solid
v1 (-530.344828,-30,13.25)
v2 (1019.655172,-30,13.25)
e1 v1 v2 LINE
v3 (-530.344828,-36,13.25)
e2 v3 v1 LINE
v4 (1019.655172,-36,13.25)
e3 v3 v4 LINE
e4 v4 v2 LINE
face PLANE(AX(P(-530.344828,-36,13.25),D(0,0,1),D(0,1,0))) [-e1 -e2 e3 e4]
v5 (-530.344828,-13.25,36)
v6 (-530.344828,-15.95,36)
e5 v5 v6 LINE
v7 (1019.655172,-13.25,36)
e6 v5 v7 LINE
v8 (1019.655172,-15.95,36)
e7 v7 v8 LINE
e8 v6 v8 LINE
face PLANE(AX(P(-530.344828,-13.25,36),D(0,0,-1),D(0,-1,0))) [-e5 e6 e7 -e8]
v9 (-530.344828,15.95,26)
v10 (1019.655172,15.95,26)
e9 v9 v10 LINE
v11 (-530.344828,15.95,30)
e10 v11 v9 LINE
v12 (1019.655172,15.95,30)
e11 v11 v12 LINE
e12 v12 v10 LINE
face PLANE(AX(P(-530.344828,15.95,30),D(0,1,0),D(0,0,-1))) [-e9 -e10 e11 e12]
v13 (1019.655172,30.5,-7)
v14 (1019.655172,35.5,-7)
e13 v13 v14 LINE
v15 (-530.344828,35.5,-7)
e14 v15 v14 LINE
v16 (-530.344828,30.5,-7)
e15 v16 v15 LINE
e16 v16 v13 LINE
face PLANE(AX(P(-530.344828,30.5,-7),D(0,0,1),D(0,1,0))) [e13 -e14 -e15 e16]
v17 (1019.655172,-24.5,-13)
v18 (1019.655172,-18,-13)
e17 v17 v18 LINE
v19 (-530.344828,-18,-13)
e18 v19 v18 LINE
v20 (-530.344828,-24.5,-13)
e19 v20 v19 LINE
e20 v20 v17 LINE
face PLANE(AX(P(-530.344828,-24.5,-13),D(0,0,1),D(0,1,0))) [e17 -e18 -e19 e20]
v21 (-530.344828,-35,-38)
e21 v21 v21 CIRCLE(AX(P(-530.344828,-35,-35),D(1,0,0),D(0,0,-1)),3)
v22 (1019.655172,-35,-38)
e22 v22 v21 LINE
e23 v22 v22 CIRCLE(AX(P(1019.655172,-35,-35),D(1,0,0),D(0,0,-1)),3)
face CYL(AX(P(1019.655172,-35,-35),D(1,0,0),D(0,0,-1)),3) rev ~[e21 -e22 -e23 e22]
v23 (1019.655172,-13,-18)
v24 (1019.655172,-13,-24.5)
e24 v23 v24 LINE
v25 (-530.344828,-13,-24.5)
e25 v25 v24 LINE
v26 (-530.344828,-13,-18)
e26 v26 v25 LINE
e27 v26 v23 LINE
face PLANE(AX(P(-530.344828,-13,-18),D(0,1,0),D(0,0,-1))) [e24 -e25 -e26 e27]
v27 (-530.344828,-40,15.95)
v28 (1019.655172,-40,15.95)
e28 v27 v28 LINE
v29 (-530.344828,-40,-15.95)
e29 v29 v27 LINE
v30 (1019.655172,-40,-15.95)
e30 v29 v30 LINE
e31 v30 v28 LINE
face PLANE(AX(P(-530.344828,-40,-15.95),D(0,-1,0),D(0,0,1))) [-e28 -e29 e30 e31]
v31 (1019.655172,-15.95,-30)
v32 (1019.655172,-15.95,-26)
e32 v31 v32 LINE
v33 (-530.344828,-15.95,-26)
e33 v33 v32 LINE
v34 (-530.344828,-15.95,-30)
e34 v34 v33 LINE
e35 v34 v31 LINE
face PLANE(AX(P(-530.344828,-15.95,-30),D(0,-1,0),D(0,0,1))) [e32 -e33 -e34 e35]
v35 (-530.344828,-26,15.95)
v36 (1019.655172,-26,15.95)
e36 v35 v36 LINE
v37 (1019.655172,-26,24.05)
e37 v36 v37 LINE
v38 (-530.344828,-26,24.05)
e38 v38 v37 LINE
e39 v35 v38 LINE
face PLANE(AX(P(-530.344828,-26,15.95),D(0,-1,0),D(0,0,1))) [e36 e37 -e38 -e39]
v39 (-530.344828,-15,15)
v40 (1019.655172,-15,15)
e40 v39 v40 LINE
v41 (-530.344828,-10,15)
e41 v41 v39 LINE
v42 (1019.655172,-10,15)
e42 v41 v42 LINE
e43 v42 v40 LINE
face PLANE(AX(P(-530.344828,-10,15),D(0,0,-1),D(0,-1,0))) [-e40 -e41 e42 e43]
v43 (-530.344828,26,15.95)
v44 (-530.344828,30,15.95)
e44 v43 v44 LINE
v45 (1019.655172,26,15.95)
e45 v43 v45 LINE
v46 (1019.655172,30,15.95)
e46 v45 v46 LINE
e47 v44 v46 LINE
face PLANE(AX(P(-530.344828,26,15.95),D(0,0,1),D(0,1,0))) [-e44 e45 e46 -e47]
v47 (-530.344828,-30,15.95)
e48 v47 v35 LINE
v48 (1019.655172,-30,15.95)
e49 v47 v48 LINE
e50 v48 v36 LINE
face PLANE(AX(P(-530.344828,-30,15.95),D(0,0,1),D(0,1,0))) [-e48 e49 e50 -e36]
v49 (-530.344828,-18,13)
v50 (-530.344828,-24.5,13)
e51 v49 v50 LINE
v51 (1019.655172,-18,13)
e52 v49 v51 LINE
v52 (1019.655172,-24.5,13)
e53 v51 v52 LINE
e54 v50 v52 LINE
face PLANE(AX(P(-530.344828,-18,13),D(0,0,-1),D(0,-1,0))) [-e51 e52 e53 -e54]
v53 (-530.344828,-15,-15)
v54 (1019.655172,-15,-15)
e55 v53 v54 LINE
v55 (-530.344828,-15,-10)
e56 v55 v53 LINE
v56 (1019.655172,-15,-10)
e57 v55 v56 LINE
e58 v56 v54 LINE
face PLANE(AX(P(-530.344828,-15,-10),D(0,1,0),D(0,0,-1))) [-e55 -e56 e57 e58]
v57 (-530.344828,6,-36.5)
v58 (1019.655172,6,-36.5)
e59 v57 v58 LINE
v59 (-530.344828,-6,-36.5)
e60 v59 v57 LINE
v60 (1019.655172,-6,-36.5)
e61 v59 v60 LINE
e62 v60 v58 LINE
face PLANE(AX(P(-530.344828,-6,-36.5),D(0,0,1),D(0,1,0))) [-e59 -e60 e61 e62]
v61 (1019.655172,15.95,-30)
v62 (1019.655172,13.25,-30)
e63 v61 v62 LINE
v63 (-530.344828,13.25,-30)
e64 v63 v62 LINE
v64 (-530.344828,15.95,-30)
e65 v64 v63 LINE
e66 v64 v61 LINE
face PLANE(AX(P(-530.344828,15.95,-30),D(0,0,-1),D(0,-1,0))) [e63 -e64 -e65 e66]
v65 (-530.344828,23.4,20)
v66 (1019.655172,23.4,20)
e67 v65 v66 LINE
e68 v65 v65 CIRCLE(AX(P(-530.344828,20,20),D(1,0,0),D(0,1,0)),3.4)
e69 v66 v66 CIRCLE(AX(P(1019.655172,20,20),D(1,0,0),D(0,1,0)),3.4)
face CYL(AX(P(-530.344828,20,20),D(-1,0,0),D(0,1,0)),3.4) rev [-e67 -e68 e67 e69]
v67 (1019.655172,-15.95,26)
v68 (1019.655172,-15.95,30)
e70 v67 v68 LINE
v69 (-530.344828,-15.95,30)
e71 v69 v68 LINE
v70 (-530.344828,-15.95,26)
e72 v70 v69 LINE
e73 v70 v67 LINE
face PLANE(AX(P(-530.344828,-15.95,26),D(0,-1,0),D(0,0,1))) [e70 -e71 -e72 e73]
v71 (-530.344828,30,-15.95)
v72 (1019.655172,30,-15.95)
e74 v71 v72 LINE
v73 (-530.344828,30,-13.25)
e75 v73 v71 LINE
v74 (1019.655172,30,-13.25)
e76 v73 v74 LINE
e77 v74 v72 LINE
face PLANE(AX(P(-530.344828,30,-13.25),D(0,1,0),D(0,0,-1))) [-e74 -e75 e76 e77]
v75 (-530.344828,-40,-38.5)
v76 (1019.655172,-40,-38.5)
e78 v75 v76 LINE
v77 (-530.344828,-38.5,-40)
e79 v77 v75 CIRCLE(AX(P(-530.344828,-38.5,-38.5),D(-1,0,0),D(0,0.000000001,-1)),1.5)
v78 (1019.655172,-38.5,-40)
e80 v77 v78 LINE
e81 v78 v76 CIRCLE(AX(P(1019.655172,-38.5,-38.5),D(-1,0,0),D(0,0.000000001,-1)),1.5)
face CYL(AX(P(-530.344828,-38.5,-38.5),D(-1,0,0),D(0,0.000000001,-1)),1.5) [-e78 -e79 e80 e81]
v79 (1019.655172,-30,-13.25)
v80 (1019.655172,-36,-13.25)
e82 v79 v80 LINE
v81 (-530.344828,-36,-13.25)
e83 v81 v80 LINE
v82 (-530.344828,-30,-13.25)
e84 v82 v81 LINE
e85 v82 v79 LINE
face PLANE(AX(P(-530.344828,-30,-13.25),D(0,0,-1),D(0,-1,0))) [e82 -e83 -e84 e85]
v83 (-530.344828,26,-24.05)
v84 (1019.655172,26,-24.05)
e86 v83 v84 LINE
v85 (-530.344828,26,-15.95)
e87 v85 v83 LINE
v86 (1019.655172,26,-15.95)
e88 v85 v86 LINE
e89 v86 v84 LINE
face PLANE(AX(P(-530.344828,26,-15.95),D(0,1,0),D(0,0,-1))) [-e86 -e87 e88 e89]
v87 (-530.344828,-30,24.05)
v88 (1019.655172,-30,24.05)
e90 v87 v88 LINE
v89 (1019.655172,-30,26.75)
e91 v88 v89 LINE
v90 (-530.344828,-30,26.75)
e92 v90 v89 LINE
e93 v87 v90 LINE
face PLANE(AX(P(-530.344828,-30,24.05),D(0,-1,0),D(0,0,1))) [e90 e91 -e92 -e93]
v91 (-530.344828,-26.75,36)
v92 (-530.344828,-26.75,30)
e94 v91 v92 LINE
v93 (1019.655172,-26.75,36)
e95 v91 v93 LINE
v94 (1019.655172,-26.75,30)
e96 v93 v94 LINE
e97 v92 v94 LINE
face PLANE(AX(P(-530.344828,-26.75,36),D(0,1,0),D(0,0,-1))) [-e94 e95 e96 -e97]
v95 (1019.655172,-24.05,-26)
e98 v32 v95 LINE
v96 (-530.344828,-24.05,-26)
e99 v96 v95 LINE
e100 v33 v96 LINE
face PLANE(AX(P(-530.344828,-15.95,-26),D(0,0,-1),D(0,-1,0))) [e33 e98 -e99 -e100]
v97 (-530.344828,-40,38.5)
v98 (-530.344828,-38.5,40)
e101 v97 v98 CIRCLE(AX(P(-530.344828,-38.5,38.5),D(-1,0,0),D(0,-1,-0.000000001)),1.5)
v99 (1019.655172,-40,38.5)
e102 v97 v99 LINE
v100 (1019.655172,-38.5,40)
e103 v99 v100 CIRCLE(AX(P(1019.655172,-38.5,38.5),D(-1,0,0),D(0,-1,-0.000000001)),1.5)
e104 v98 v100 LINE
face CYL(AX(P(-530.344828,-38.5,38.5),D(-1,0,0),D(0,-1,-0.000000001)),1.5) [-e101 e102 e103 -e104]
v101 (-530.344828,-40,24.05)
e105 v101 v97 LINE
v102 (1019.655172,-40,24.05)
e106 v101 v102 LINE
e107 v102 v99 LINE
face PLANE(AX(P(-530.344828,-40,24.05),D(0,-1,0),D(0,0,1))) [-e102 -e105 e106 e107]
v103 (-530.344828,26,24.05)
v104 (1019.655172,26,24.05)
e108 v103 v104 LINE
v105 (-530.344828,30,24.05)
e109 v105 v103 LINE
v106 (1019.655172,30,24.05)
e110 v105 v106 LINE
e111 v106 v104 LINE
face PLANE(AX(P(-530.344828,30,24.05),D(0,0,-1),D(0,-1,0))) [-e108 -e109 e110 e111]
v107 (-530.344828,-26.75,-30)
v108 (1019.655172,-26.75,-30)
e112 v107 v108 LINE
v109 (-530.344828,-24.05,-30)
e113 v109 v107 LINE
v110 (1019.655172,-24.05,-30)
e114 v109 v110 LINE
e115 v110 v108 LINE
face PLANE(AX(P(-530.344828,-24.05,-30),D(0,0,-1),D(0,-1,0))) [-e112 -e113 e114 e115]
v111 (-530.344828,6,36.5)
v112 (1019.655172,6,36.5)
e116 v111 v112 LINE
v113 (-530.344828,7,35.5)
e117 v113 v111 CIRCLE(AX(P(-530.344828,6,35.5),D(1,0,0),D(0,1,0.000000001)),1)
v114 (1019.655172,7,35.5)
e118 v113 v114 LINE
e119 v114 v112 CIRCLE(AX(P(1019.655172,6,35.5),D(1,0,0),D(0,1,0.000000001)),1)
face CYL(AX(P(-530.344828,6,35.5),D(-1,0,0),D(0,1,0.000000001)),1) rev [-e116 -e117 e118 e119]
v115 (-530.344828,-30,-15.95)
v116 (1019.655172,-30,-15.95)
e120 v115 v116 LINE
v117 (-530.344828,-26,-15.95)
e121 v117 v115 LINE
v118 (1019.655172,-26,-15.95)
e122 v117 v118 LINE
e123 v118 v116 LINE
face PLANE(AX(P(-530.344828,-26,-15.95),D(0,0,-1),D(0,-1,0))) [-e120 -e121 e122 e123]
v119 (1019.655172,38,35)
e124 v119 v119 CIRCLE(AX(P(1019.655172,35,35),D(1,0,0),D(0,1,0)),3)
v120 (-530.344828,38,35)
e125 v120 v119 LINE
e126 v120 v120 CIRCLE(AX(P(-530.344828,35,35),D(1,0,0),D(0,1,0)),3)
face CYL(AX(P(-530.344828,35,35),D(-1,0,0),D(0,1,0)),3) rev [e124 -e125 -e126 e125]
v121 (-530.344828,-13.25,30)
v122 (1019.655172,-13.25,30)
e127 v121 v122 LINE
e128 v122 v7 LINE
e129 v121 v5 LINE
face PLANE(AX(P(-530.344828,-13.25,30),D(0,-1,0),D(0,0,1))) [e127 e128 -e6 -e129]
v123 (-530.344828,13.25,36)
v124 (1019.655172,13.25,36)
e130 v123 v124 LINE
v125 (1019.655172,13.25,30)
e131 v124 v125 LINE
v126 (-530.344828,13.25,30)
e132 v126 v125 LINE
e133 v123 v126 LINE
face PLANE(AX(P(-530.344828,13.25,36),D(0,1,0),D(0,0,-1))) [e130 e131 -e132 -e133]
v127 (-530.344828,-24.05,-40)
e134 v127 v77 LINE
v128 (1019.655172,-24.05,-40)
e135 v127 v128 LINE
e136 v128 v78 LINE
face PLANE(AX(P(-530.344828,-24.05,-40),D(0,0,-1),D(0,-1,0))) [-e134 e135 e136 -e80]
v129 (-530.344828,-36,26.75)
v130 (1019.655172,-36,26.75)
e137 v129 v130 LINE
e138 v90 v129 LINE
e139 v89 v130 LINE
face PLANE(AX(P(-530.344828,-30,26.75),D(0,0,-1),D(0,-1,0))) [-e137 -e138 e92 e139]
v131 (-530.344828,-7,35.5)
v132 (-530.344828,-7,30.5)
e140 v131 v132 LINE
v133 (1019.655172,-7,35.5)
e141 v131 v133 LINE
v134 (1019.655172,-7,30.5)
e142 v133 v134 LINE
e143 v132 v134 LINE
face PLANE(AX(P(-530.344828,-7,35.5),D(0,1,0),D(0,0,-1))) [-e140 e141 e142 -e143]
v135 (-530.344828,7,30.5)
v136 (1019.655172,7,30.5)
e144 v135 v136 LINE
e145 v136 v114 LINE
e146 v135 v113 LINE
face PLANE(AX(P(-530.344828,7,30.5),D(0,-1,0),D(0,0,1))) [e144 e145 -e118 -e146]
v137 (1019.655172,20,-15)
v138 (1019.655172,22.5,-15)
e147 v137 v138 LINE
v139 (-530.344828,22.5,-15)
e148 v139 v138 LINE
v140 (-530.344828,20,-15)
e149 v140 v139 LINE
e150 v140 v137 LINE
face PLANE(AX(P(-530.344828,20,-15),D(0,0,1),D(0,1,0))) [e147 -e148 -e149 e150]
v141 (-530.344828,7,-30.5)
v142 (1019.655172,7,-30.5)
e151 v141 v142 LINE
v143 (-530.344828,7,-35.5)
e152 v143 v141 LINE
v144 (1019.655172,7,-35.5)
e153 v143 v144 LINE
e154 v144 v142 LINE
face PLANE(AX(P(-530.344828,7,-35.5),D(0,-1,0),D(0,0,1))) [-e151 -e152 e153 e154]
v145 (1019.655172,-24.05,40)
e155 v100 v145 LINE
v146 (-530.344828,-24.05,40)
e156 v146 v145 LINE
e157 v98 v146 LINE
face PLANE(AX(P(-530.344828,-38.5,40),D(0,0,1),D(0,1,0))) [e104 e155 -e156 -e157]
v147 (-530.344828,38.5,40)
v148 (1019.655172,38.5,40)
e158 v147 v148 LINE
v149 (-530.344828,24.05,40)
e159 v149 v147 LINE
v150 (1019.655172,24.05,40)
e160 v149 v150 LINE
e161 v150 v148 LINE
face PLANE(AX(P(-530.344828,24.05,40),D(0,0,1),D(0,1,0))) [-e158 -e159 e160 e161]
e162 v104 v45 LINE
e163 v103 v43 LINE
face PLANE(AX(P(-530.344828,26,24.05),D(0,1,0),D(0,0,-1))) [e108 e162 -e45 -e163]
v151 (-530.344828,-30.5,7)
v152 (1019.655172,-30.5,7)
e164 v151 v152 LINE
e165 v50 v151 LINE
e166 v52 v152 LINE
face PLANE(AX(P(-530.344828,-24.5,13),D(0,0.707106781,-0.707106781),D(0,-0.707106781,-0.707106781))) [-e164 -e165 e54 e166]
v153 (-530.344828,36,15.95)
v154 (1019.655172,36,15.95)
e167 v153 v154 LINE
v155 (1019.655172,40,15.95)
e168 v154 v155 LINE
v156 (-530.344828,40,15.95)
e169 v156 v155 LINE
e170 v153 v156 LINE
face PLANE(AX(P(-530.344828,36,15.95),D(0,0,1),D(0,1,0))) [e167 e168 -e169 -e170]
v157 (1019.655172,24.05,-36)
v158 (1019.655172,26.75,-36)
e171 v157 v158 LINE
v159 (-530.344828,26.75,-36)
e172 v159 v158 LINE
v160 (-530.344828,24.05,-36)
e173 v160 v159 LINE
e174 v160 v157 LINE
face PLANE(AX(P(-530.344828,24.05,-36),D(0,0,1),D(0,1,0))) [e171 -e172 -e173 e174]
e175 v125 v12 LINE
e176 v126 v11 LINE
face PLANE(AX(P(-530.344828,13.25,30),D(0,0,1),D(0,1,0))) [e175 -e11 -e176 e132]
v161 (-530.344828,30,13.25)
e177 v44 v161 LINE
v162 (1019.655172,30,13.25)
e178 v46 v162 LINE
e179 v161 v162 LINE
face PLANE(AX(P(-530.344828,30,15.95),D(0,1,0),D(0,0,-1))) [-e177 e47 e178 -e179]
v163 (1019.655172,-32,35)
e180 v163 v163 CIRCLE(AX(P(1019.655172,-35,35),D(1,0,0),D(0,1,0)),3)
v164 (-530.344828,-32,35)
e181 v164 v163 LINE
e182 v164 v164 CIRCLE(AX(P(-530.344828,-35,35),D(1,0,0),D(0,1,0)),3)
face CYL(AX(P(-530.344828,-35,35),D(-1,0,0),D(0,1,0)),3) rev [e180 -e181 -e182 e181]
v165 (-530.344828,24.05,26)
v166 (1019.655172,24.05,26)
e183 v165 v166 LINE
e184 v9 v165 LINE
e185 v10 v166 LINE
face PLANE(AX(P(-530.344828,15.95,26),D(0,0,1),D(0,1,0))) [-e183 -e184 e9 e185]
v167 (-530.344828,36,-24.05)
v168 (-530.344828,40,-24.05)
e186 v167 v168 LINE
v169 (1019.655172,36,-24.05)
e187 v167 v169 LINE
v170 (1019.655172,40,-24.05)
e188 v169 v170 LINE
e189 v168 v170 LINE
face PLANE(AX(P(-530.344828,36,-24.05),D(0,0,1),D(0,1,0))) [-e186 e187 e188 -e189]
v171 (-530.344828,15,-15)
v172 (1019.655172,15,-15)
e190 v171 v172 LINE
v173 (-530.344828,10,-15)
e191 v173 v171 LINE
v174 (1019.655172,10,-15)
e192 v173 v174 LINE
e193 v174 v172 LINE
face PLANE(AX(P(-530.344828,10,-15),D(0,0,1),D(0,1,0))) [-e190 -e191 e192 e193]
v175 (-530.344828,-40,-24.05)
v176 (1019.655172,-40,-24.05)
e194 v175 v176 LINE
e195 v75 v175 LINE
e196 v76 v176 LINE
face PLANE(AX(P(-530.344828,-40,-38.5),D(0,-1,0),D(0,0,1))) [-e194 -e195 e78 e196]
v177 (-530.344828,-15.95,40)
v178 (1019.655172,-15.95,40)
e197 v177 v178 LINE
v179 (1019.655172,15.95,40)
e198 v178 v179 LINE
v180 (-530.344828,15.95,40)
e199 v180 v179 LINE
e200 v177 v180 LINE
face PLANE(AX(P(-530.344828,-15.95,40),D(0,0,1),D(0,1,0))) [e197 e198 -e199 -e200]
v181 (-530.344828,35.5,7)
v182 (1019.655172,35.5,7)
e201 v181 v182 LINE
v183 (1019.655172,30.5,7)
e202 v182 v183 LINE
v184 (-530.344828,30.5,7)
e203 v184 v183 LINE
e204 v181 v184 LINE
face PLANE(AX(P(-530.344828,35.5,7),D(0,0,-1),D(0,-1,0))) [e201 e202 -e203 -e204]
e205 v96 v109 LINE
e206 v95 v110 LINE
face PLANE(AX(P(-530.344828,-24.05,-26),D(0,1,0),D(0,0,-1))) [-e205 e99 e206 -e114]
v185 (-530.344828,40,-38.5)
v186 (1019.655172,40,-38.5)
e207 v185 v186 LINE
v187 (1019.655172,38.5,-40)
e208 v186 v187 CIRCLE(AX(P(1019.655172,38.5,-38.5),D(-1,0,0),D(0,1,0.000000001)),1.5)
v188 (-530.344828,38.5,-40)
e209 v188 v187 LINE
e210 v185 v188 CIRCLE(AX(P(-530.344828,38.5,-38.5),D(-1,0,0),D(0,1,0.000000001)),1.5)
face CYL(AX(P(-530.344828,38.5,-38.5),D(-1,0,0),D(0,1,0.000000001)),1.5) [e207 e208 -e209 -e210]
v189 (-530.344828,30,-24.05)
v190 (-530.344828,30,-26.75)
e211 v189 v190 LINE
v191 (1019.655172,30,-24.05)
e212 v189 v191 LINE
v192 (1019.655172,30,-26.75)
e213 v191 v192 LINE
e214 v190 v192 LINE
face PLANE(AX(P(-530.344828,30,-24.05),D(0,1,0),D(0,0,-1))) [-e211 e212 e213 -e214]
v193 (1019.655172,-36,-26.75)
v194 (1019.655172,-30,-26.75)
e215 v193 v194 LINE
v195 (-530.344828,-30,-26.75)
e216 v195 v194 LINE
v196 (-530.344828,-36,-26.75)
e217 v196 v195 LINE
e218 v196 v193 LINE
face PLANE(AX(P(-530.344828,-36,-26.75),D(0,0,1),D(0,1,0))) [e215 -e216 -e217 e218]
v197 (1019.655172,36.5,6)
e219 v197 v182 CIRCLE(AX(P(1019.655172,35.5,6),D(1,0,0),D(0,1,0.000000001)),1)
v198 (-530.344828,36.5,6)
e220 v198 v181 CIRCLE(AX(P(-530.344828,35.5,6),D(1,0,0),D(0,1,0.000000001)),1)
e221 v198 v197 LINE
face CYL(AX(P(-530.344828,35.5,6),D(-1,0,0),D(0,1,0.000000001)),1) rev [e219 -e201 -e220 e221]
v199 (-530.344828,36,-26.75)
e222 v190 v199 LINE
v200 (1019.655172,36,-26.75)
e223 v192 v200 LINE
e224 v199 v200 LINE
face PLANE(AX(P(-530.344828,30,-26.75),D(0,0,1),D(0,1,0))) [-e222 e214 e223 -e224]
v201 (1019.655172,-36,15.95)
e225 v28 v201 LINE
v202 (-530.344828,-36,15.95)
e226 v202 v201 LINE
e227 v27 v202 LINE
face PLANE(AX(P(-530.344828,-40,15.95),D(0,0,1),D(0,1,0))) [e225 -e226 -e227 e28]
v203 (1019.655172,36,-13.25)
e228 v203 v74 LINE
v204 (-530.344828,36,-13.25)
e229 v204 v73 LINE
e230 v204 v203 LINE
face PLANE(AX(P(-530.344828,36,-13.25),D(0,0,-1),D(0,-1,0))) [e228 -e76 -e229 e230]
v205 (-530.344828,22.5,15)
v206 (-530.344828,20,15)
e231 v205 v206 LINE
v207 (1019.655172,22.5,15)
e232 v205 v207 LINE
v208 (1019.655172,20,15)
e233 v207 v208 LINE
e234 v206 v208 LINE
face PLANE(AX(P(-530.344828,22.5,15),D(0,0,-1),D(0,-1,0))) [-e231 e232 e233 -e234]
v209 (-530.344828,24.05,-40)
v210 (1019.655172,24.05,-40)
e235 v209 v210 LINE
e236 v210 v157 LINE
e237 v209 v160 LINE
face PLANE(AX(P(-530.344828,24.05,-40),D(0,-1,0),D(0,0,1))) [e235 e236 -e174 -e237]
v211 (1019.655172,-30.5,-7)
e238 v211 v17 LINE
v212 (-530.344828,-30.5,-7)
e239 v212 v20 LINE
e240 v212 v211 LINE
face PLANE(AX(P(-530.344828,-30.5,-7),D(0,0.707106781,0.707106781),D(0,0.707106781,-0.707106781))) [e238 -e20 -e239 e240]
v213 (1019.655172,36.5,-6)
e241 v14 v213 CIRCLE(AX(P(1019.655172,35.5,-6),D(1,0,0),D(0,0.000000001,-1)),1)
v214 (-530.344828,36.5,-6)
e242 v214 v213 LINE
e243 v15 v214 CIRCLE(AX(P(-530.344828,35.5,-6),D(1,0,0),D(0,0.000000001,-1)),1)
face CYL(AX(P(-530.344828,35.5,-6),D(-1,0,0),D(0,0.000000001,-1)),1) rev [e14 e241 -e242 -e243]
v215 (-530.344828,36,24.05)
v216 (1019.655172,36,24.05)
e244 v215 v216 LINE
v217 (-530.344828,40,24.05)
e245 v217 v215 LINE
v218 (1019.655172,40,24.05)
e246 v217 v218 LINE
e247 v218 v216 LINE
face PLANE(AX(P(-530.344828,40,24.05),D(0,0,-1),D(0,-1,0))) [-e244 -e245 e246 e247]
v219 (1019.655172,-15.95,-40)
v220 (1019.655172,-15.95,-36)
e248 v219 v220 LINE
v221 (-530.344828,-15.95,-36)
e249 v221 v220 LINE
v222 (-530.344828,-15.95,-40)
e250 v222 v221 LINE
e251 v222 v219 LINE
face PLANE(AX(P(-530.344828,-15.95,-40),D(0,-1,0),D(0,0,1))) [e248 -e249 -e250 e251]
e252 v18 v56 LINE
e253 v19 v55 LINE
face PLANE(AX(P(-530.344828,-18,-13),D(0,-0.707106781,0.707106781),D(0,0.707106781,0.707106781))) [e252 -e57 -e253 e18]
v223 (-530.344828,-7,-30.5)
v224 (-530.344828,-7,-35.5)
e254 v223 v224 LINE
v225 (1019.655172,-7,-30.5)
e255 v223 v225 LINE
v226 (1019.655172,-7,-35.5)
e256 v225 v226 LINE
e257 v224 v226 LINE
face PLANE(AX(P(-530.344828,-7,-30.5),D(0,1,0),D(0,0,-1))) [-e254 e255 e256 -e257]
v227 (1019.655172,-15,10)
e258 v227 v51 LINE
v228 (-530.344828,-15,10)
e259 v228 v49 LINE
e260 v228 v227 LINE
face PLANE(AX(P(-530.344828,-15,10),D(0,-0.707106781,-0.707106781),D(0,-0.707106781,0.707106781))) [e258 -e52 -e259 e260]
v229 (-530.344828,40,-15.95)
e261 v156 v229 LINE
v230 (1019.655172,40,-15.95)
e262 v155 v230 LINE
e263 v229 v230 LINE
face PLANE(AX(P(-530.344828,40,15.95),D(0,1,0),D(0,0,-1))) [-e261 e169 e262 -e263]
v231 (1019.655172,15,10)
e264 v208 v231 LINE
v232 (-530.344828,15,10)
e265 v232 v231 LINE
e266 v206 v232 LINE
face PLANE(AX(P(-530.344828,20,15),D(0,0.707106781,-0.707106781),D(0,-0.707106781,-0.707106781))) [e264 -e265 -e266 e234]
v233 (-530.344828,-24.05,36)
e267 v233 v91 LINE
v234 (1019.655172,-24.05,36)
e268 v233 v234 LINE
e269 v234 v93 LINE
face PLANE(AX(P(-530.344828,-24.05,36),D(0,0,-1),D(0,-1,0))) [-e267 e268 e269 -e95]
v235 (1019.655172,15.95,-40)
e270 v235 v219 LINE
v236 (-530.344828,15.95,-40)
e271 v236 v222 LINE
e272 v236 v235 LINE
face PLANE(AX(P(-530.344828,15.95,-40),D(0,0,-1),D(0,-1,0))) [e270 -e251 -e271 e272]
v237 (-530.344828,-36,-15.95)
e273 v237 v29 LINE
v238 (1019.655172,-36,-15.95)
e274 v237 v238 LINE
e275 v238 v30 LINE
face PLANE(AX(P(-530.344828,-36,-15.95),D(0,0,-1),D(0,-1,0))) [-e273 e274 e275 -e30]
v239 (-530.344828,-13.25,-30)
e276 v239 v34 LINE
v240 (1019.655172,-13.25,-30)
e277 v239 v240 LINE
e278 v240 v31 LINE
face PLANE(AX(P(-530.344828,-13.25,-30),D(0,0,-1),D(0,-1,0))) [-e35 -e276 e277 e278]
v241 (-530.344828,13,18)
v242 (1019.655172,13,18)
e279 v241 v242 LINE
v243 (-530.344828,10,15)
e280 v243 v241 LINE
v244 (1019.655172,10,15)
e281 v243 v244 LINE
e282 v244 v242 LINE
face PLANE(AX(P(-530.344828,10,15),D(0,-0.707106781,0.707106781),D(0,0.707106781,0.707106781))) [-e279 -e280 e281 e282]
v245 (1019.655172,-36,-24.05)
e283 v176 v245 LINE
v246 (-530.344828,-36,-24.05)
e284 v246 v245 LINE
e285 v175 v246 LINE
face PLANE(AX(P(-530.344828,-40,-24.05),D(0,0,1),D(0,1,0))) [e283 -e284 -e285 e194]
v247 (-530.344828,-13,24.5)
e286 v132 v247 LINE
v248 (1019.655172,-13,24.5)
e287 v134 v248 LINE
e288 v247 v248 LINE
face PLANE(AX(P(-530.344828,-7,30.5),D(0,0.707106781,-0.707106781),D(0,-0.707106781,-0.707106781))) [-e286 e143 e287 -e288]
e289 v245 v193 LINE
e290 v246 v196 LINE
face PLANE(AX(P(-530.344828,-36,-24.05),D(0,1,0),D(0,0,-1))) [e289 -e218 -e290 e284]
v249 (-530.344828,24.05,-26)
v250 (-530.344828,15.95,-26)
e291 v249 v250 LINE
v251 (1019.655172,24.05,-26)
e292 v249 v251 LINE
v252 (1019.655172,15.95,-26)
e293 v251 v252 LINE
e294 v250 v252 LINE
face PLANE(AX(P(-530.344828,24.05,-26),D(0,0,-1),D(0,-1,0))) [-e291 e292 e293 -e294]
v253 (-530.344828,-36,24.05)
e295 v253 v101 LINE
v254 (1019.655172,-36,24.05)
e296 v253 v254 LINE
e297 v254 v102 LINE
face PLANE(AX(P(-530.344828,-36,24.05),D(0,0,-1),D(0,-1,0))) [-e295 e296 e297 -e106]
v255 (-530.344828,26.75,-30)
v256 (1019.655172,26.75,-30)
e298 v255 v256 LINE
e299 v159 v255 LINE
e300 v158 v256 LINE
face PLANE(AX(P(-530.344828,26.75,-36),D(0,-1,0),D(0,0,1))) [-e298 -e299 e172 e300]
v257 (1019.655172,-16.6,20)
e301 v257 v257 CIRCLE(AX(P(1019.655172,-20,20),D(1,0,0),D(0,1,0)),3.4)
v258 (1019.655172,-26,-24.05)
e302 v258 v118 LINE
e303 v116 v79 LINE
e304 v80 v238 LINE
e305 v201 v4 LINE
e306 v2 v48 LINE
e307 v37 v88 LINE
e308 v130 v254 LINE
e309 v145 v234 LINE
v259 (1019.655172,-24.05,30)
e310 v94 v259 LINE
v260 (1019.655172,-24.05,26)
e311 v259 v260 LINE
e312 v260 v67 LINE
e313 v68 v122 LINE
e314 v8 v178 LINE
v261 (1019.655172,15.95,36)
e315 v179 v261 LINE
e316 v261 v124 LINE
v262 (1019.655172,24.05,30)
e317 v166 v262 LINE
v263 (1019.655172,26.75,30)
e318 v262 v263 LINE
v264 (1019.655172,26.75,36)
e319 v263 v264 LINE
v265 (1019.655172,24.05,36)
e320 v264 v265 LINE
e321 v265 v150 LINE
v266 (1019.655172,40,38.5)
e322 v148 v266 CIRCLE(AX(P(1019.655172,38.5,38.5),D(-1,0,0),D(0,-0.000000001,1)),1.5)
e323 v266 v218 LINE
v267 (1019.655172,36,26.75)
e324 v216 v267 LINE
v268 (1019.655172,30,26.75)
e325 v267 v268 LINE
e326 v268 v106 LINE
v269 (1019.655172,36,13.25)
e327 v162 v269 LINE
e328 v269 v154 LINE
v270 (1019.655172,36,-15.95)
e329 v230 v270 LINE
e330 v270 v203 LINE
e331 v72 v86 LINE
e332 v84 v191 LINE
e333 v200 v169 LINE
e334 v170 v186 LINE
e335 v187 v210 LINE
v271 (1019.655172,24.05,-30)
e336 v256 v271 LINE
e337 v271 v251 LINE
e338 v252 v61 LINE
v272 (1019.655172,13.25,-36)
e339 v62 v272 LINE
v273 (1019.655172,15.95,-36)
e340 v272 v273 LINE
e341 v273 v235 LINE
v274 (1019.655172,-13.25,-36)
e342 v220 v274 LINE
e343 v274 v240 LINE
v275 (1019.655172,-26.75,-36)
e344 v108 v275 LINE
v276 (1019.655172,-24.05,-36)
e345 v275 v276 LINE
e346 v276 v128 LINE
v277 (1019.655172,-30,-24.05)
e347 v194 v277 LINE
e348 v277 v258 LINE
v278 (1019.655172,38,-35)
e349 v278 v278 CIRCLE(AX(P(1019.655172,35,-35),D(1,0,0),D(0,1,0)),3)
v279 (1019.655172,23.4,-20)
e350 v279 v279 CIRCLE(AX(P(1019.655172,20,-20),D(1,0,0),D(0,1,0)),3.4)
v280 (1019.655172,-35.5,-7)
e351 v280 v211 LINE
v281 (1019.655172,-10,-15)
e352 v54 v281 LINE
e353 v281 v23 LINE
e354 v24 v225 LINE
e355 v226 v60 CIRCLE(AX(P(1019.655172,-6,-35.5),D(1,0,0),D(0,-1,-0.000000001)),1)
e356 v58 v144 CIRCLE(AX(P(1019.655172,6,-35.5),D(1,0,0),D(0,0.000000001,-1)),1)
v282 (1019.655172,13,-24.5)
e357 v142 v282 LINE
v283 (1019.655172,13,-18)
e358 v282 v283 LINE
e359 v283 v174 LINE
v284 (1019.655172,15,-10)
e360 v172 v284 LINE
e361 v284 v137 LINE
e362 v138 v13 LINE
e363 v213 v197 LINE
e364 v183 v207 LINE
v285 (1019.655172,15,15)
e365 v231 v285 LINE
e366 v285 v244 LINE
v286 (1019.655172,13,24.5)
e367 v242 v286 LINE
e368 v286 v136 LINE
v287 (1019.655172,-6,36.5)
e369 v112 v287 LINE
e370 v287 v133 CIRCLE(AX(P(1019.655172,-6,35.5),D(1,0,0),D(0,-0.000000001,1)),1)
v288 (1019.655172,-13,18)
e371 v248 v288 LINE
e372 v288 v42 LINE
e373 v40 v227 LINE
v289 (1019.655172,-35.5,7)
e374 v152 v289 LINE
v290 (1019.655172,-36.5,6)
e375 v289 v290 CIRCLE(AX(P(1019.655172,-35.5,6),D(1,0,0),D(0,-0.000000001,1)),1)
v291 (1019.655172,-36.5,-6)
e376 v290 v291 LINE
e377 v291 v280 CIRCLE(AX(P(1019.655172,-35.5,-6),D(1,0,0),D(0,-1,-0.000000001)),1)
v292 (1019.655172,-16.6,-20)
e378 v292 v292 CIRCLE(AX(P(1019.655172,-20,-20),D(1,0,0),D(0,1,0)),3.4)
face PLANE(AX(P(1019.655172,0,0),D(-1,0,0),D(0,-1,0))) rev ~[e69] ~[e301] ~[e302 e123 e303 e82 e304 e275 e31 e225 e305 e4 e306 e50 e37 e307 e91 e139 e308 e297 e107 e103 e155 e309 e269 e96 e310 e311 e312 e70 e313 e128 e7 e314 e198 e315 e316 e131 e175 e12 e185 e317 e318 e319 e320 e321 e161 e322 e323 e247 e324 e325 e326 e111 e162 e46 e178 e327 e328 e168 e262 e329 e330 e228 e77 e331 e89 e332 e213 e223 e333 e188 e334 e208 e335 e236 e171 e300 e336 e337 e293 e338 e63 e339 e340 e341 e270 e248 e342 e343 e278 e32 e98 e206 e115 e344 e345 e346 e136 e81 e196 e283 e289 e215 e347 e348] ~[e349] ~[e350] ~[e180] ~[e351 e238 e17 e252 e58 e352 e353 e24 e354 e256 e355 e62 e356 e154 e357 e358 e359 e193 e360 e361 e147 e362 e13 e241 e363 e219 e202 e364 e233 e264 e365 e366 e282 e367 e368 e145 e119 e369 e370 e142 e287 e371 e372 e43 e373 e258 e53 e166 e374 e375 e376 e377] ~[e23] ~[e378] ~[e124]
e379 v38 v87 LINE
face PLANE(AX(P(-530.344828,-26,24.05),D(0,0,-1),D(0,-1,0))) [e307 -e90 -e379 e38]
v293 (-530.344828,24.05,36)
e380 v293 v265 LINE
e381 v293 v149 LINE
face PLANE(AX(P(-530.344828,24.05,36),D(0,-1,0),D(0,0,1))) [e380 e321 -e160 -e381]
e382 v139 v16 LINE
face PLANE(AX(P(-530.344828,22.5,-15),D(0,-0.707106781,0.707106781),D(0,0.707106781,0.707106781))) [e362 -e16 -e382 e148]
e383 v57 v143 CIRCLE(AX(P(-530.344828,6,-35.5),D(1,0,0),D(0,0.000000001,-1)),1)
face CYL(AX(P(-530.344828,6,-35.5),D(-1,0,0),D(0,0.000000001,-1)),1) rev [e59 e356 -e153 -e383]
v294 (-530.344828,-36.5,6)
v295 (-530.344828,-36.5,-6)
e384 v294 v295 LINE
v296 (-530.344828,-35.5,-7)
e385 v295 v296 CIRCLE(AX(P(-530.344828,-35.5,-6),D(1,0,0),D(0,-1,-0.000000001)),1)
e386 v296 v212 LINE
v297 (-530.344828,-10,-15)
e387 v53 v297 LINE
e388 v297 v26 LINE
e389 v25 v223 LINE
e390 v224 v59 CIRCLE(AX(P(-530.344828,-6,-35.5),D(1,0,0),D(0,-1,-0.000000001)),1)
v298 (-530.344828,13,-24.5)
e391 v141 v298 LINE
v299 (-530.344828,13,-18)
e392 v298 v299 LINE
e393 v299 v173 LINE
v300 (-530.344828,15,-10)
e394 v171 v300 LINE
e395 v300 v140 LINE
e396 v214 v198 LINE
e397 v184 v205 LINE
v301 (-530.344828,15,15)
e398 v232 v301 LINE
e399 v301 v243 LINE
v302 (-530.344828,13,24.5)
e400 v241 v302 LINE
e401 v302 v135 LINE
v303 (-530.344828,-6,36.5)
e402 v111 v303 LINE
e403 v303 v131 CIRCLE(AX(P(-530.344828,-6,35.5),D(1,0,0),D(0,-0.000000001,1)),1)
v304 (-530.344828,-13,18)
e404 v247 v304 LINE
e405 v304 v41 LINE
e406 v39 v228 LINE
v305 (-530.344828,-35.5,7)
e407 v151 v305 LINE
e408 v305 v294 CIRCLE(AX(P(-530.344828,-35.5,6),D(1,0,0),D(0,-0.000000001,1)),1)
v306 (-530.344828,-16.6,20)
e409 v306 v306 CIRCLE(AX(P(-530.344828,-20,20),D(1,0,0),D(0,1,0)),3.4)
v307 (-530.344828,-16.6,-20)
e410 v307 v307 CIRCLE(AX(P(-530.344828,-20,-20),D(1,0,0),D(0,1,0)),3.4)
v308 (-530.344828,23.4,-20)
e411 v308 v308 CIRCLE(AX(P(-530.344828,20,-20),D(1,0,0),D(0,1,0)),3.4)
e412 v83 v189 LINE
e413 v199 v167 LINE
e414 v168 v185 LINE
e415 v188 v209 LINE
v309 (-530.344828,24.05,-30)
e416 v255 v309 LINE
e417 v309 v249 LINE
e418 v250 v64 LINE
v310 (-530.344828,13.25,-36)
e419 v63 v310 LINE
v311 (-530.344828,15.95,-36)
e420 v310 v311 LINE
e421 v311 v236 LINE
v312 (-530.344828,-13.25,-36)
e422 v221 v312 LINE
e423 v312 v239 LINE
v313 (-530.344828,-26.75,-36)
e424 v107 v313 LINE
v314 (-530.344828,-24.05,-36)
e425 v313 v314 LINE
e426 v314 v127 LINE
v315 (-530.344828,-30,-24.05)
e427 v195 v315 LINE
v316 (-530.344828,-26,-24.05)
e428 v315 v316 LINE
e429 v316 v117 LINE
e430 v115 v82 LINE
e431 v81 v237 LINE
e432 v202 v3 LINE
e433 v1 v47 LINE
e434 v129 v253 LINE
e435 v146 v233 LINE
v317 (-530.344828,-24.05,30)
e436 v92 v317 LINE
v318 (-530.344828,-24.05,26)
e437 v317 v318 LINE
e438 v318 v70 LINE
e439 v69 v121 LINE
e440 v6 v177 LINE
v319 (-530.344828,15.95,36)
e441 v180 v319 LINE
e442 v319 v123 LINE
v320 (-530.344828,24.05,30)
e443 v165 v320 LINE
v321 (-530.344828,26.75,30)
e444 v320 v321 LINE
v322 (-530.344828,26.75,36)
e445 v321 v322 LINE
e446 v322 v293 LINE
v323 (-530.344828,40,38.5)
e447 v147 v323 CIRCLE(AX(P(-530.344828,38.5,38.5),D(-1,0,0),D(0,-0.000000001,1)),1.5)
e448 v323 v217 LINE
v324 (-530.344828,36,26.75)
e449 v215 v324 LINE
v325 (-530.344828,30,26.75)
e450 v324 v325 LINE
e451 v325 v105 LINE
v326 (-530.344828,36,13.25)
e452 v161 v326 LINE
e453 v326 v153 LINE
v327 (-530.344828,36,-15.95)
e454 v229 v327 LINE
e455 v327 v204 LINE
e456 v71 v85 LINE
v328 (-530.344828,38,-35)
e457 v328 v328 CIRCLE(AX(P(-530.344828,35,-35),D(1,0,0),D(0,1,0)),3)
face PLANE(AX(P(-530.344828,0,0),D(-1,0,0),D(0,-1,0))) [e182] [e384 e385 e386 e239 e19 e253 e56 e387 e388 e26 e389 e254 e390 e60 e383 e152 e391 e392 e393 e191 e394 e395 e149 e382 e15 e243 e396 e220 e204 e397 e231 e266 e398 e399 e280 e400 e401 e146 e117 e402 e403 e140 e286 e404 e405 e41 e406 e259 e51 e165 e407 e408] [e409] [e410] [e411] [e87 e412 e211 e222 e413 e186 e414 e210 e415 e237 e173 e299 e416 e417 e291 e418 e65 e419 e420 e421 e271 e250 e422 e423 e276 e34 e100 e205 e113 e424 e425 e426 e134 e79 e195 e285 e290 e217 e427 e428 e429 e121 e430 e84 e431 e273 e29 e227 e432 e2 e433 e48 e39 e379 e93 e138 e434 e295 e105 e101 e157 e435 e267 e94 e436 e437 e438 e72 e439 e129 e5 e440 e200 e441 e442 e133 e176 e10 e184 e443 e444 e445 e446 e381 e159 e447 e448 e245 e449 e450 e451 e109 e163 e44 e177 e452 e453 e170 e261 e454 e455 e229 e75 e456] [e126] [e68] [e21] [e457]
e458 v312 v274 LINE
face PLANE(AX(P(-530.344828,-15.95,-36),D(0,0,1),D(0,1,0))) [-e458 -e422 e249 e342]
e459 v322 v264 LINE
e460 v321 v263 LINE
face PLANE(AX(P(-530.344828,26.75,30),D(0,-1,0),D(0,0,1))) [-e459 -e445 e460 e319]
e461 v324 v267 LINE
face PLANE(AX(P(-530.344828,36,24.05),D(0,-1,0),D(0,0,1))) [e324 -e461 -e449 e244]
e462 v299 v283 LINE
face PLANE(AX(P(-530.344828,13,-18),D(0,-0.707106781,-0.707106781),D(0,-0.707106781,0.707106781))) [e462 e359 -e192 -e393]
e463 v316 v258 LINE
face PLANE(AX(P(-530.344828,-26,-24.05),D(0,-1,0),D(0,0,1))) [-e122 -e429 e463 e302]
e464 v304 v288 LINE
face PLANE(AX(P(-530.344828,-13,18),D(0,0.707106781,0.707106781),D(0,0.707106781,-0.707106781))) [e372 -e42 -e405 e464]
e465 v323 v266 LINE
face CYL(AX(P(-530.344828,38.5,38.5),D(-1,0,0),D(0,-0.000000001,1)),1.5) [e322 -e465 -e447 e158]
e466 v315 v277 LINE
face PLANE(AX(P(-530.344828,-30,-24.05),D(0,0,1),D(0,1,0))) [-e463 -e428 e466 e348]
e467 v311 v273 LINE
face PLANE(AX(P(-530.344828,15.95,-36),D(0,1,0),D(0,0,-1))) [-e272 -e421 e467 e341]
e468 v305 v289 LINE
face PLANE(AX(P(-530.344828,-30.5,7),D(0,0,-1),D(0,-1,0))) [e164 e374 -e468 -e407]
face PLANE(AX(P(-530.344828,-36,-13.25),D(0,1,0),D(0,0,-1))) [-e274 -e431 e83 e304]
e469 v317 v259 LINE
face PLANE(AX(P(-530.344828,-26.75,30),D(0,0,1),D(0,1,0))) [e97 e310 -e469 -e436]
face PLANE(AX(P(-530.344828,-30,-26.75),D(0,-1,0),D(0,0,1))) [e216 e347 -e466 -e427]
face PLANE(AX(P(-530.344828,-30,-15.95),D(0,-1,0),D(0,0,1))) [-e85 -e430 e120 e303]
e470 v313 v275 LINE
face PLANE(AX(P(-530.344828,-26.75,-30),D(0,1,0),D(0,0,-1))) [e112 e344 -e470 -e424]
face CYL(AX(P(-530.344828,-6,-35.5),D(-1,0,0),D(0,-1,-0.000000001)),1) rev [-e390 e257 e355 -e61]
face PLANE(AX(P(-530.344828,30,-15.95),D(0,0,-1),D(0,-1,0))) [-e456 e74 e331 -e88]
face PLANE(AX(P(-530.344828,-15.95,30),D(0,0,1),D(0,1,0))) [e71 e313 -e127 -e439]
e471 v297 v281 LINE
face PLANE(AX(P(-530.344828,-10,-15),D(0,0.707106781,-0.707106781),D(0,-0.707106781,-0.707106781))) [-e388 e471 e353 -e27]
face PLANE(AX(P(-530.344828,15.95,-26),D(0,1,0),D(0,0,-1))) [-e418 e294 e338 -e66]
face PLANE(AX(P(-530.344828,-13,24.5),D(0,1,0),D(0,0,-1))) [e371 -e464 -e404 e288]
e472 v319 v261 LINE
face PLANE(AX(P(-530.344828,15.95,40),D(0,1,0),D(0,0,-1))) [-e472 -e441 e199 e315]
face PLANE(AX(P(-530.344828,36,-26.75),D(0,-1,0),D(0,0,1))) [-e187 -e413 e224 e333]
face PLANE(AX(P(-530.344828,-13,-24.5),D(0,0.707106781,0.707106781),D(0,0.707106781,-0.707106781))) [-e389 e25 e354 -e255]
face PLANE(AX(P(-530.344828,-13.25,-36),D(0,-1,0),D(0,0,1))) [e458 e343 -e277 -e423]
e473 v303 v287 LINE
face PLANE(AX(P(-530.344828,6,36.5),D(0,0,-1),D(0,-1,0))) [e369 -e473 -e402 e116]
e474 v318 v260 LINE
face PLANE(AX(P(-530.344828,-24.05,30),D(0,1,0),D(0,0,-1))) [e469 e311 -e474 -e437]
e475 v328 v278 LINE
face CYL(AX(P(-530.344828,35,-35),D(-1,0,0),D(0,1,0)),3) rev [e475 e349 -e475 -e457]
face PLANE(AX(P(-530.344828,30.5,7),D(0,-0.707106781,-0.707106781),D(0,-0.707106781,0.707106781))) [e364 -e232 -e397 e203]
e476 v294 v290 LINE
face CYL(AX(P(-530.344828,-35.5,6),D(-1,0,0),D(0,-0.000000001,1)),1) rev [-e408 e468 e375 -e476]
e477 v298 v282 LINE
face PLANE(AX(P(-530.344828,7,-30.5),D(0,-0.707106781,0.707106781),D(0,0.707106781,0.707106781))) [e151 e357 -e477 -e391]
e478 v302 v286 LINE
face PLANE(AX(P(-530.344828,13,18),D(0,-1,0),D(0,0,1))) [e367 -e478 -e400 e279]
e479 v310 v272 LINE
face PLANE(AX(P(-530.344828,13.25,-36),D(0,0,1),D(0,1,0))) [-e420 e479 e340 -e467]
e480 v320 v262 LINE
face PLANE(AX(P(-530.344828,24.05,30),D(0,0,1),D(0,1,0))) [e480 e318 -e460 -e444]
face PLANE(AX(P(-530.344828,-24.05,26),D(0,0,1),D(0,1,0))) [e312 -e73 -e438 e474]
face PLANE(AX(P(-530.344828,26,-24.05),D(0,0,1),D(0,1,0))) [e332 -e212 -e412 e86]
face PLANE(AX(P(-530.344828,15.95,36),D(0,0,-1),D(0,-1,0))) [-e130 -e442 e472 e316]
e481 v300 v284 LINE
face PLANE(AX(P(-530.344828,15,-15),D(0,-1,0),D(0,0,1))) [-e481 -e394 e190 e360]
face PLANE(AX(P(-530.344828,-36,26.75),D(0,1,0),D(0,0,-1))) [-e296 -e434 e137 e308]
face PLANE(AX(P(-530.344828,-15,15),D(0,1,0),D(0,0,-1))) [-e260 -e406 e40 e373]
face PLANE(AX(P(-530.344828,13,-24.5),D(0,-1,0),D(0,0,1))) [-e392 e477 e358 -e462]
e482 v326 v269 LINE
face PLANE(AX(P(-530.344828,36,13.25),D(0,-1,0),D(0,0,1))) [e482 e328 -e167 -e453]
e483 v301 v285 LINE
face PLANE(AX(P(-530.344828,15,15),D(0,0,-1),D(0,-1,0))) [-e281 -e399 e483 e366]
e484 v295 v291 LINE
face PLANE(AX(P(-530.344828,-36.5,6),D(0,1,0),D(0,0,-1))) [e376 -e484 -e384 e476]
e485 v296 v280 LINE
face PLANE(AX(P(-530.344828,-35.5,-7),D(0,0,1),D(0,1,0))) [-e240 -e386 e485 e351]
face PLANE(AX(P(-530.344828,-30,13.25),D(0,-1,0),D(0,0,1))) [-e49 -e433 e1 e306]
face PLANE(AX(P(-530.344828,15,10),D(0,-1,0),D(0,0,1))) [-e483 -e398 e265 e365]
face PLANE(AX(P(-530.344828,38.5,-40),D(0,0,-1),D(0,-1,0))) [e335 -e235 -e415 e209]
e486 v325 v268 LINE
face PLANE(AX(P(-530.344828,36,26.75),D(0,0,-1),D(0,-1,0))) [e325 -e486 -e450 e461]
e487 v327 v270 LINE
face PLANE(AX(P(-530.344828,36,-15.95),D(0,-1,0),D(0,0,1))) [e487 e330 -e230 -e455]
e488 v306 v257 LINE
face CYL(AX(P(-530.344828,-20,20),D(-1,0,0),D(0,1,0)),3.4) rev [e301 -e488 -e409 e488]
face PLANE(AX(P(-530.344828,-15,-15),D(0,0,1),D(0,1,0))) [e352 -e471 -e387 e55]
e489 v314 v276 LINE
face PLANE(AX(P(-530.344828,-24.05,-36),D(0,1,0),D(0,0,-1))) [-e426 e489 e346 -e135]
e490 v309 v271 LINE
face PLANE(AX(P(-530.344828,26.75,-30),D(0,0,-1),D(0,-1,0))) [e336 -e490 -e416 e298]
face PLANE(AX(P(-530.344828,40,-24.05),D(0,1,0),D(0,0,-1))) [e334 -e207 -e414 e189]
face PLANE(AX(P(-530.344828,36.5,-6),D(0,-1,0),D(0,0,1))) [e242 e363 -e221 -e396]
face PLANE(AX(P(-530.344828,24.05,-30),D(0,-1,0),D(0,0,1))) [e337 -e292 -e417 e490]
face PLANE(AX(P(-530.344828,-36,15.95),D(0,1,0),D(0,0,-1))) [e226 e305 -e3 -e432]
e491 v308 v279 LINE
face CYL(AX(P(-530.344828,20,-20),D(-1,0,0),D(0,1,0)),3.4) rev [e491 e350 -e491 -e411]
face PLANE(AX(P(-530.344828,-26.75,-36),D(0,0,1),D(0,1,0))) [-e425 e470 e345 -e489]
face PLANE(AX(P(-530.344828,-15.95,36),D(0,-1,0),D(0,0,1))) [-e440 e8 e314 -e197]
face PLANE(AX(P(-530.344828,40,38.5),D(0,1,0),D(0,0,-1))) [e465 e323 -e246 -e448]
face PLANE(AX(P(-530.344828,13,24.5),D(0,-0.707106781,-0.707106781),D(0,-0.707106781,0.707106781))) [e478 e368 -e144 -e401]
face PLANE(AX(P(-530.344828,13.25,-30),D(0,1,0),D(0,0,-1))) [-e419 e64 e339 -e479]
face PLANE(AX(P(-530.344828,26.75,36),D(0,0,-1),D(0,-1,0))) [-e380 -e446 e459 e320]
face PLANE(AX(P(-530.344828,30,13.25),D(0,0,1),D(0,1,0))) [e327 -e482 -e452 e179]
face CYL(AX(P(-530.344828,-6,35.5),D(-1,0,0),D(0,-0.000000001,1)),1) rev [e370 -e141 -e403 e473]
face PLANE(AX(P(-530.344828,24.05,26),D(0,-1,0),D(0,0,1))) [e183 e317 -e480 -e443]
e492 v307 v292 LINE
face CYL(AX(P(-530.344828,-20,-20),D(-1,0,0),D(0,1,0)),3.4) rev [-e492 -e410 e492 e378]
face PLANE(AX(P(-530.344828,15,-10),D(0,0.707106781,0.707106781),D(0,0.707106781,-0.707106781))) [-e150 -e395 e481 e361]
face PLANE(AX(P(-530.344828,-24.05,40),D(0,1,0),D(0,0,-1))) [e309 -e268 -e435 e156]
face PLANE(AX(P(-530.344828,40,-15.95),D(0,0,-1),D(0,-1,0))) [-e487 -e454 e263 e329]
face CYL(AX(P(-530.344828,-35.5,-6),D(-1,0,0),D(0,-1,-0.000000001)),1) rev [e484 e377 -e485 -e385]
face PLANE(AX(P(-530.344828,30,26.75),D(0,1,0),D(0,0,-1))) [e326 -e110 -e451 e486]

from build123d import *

# Parameters (mm, degrees)
SKETCH1_R                                 = 3.4
SKETCH1_R_2                               = 3
ALUMINIUM_PROFILE_80_X_80G_X_R1_5_1_DEPTH = 1550
SKETCH10_R                                = 3
CUT_EXTRUDE1_DEPTH                        = 1552.031914565


with BuildPart() as part:
    # Sketch1 → Aluminium profile 80 X 80G X R1.5(1) (new body)
    with BuildSketch(Plane.YZ.offset(-530.344827586)):
        with BuildLine():
            Line((-24.05, 40), (-24.05, 36))
            Line((-24.05, 36), (-26.75, 36))
            Line((-26.75, 36), (-26.75, 30))
            Line((-26.75, 30), (-24.05, 30))
            Line((-24.05, 30), (-24.05, 26))
            Line((-24.05, 26), (-15.95, 26))
            Line((-15.95, 26), (-15.95, 30))
            Line((-15.95, 30), (-13.25, 30))
            Line((-13.25, 30), (-13.25, 36))
            Line((-13.25, 36), (-15.95, 36))
            Line((-15.95, 36), (-15.95, 40))
            Line((-15.95, 40), (15.95, 40))
            Line((15.95, 40), (15.95, 36))
            Line((15.95, 36), (13.25, 36))
            Line((13.25, 36), (13.25, 30))
            Line((13.25, 30), (15.95, 30))
            Line((15.95, 30), (15.95, 26))
            Line((15.95, 26), (24.05, 26))
            Line((24.05, 26), (24.05, 30))
            Line((24.05, 30), (26.75, 30))
            Line((26.75, 30), (26.75, 36))
            Line((26.75, 36), (24.05, 36))
            Line((24.05, 36), (24.05, 40))
            Line((24.05, 40), (38.5, 40))
            ThreePointArc((38.5, 40), (39.560660172, 39.560660172), (40, 38.5))
            Line((40, 38.5), (40, 24.05))
            Line((40, 24.05), (36, 24.05))
            Line((36, 24.05), (36, 26.75))
            Line((36, 26.75), (30, 26.75))
            Line((30, 26.75), (30, 24.05))
            Line((30, 24.05), (26, 24.05))
            Line((26, 24.05), (26, 15.95))
            Line((26, 15.95), (30, 15.95))
            Line((30, 15.95), (30, 13.25))
            Line((30, 13.25), (36, 13.25))
            Line((36, 13.25), (36, 15.95))
            Line((36, 15.95), (40, 15.95))
            Line((40, 15.95), (40, -15.95))
            Line((40, -15.95), (36, -15.95))
            Line((36, -15.95), (36, -13.25))
            Line((36, -13.25), (30, -13.25))
            Line((30, -13.25), (30, -15.95))
            Line((30, -15.95), (26, -15.95))
            Line((26, -15.95), (26, -24.05))
            Line((26, -24.05), (30, -24.05))
            Line((30, -24.05), (30, -26.75))
            Line((30, -26.75), (36, -26.75))
            Line((36, -26.75), (36, -24.05))
            Line((36, -24.05), (40, -24.05))
            Line((40, -24.05), (40, -38.5))
            ThreePointArc((40, -38.5), (39.560660172, -39.560660172), (38.5, -40))
            Line((38.5, -40), (24.05, -40))
            Line((24.05, -40), (24.05, -36))
            Line((24.05, -36), (26.75, -36))
            Line((26.75, -36), (26.75, -30))
            Line((26.75, -30), (24.05, -30))
            Line((24.05, -30), (24.05, -26))
            Line((24.05, -26), (15.95, -26))
            Line((15.95, -26), (15.95, -30))
            Line((15.95, -30), (13.25, -30))
            Line((13.25, -30), (13.25, -36))
            Line((13.25, -36), (15.95, -36))
            Line((15.95, -36), (15.95, -40))
            Line((15.95, -40), (-15.95, -40))
            Line((-15.95, -40), (-15.95, -36))
            Line((-15.95, -36), (-13.25, -36))
            Line((-13.25, -36), (-13.25, -30))
            Line((-13.25, -30), (-15.95, -30))
            Line((-15.95, -30), (-15.95, -26))
            Line((-15.95, -26), (-24.05, -26))
            Line((-24.05, -26), (-24.05, -30))
            Line((-24.05, -30), (-26.75, -30))
            Line((-26.75, -30), (-26.75, -36))
            Line((-26.75, -36), (-24.05, -36))
            Line((-24.05, -36), (-24.05, -40))
            Line((-24.05, -40), (-38.5, -40))
            ThreePointArc((-38.5, -40), (-39.560660172, -39.560660172), (-40, -38.5))
            Line((-40, -38.5), (-40, -24.05))
            Line((-40, -24.05), (-36, -24.05))
            Line((-36, -24.05), (-36, -26.75))
            Line((-36, -26.75), (-30, -26.75))
            Line((-30, -26.75), (-30, -24.05))
            Line((-30, -24.05), (-26, -24.05))
            Line((-26, -24.05), (-26, -15.95))
            Line((-26, -15.95), (-30, -15.95))
            Line((-30, -15.95), (-30, -13.25))
            Line((-30, -13.25), (-36, -13.25))
            Line((-36, -13.25), (-36, -15.95))
            Line((-36, -15.95), (-40, -15.95))
            Line((-40, -15.95), (-40, 15.95))
            Line((-40, 15.95), (-36, 15.95))
            Line((-36, 15.95), (-36, 13.25))
            Line((-36, 13.25), (-30, 13.25))
            Line((-30, 13.25), (-30, 15.95))
            Line((-30, 15.95), (-26, 15.95))
            Line((-26, 15.95), (-26, 24.05))
            Line((-26, 24.05), (-30, 24.05))
            Line((-30, 24.05), (-30, 26.75))
            Line((-30, 26.75), (-36, 26.75))
            Line((-36, 26.75), (-36, 24.05))
            Line((-36, 24.05), (-40, 24.05))
            Line((-40, 24.05), (-40, 38.5))
            ThreePointArc((-40, 38.5), (-39.560660172, 39.560660172), (-38.5, 40))
            Line((-38.5, 40), (-24.05, 40))
        make_face()
        with Locations((-20, 20)):
            Circle(SKETCH1_R, mode=Mode.SUBTRACT)
        with Locations((20, 20)):
            Circle(SKETCH1_R, mode=Mode.SUBTRACT)
        with Locations((20, -20)):
            Circle(SKETCH1_R, mode=Mode.SUBTRACT)
        with Locations((-20, -20)):
            Circle(SKETCH1_R, mode=Mode.SUBTRACT)
        with Locations((-35, 35)):
            Circle(SKETCH1_R_2, mode=Mode.SUBTRACT)
        with Locations((35, 35)):
            Circle(SKETCH1_R_2, mode=Mode.SUBTRACT)
        with Locations((35, -35)):
            Circle(SKETCH1_R_2, mode=Mode.SUBTRACT)
        with BuildLine():
            Line((-13, 18), (-10, 15))
            Line((-10, 15), (-15, 15))
            Line((-15, 15), (-15, 10))
            Line((-15, 10), (-18, 13))
            Line((-18, 13), (-24.5, 13))
            Line((-24.5, 13), (-30.5, 7))
            Line((-30.5, 7), (-35.5, 7))
            ThreePointArc((-35.5, 7), (-36.207106781, 6.707106781), (-36.5, 6))
            Line((-36.5, 6), (-36.5, -6))
            ThreePointArc((-36.5, -6), (-36.207106781, -6.707106781), (-35.5, -7))
            Line((-35.5, -7), (-30.5, -7))
            Line((-30.5, -7), (-24.5, -13))
            Line((-24.5, -13), (-18, -13))
            Line((-18, -13), (-15, -10))
            Line((-15, -10), (-15, -15))
            Line((-15, -15), (-10, -15))
            Line((-10, -15), (-13, -18))
            Line((-13, -18), (-13, -24.5))
            Line((-13, -24.5), (-7, -30.5))
            Line((-7, -30.5), (-7, -35.5))
            ThreePointArc((-7, -35.5), (-6.707106781, -36.207106781), (-6, -36.5))
            Line((-6, -36.5), (6, -36.5))
            ThreePointArc((6, -36.5), (6.707106781, -36.207106781), (7, -35.5))
            Line((7, -35.5), (7, -30.5))
            Line((7, -30.5), (13, -24.5))
            Line((13, -24.5), (13, -18))
            Line((13, -18), (10, -15))
            Line((10, -15), (15, -15))
            Line((15, -15), (15, -10))
            Line((15, -10), (20, -15))
            Line((20, -15), (22.5, -15))
            Line((22.5, -15), (30.5, -7))
            Line((30.5, -7), (35.5, -7))
            ThreePointArc((35.5, -7), (36.207106781, -6.707106781), (36.5, -6))
            Line((36.5, -6), (36.5, 6))
            ThreePointArc((36.5, 6), (36.207106781, 6.707106781), (35.5, 7))
            Line((35.5, 7), (30.5, 7))
            Line((30.5, 7), (22.5, 15))
            Line((22.5, 15), (20, 15))
            Line((20, 15), (15, 10))
            Line((15, 10), (15, 15))
            Line((15, 15), (10, 15))
            Line((10, 15), (13, 18))
            Line((13, 18), (13, 24.5))
            Line((13, 24.5), (7, 30.5))
            Line((7, 30.5), (7, 35.5))
            ThreePointArc((7, 35.5), (6.707106781, 36.207106781), (6, 36.5))
            Line((6, 36.5), (-6, 36.5))
            ThreePointArc((-6, 36.5), (-6.707106781, 36.207106781), (-7, 35.5))
            Line((-7, 35.5), (-7, 30.5))
            Line((-7, 30.5), (-13, 24.5))
            Line((-13, 24.5), (-13, 18))
        make_face(mode=Mode.SUBTRACT)
    extrude(amount=ALUMINIUM_PROFILE_80_X_80G_X_R1_5_1_DEPTH)

    # Sketch10 → Cut-Extrude1 (cut, through all)
    with BuildSketch(Plane(origin=(1019.655172414, 0, 0), x_dir=(0, 0, -1), z_dir=(1, 0, 0))):
        with Locations((35, -35)):
            Circle(SKETCH10_R)
    extrude(amount=-CUT_EXTRUDE1_DEPTH, mode=Mode.SUBTRACT)


solid = part.part
